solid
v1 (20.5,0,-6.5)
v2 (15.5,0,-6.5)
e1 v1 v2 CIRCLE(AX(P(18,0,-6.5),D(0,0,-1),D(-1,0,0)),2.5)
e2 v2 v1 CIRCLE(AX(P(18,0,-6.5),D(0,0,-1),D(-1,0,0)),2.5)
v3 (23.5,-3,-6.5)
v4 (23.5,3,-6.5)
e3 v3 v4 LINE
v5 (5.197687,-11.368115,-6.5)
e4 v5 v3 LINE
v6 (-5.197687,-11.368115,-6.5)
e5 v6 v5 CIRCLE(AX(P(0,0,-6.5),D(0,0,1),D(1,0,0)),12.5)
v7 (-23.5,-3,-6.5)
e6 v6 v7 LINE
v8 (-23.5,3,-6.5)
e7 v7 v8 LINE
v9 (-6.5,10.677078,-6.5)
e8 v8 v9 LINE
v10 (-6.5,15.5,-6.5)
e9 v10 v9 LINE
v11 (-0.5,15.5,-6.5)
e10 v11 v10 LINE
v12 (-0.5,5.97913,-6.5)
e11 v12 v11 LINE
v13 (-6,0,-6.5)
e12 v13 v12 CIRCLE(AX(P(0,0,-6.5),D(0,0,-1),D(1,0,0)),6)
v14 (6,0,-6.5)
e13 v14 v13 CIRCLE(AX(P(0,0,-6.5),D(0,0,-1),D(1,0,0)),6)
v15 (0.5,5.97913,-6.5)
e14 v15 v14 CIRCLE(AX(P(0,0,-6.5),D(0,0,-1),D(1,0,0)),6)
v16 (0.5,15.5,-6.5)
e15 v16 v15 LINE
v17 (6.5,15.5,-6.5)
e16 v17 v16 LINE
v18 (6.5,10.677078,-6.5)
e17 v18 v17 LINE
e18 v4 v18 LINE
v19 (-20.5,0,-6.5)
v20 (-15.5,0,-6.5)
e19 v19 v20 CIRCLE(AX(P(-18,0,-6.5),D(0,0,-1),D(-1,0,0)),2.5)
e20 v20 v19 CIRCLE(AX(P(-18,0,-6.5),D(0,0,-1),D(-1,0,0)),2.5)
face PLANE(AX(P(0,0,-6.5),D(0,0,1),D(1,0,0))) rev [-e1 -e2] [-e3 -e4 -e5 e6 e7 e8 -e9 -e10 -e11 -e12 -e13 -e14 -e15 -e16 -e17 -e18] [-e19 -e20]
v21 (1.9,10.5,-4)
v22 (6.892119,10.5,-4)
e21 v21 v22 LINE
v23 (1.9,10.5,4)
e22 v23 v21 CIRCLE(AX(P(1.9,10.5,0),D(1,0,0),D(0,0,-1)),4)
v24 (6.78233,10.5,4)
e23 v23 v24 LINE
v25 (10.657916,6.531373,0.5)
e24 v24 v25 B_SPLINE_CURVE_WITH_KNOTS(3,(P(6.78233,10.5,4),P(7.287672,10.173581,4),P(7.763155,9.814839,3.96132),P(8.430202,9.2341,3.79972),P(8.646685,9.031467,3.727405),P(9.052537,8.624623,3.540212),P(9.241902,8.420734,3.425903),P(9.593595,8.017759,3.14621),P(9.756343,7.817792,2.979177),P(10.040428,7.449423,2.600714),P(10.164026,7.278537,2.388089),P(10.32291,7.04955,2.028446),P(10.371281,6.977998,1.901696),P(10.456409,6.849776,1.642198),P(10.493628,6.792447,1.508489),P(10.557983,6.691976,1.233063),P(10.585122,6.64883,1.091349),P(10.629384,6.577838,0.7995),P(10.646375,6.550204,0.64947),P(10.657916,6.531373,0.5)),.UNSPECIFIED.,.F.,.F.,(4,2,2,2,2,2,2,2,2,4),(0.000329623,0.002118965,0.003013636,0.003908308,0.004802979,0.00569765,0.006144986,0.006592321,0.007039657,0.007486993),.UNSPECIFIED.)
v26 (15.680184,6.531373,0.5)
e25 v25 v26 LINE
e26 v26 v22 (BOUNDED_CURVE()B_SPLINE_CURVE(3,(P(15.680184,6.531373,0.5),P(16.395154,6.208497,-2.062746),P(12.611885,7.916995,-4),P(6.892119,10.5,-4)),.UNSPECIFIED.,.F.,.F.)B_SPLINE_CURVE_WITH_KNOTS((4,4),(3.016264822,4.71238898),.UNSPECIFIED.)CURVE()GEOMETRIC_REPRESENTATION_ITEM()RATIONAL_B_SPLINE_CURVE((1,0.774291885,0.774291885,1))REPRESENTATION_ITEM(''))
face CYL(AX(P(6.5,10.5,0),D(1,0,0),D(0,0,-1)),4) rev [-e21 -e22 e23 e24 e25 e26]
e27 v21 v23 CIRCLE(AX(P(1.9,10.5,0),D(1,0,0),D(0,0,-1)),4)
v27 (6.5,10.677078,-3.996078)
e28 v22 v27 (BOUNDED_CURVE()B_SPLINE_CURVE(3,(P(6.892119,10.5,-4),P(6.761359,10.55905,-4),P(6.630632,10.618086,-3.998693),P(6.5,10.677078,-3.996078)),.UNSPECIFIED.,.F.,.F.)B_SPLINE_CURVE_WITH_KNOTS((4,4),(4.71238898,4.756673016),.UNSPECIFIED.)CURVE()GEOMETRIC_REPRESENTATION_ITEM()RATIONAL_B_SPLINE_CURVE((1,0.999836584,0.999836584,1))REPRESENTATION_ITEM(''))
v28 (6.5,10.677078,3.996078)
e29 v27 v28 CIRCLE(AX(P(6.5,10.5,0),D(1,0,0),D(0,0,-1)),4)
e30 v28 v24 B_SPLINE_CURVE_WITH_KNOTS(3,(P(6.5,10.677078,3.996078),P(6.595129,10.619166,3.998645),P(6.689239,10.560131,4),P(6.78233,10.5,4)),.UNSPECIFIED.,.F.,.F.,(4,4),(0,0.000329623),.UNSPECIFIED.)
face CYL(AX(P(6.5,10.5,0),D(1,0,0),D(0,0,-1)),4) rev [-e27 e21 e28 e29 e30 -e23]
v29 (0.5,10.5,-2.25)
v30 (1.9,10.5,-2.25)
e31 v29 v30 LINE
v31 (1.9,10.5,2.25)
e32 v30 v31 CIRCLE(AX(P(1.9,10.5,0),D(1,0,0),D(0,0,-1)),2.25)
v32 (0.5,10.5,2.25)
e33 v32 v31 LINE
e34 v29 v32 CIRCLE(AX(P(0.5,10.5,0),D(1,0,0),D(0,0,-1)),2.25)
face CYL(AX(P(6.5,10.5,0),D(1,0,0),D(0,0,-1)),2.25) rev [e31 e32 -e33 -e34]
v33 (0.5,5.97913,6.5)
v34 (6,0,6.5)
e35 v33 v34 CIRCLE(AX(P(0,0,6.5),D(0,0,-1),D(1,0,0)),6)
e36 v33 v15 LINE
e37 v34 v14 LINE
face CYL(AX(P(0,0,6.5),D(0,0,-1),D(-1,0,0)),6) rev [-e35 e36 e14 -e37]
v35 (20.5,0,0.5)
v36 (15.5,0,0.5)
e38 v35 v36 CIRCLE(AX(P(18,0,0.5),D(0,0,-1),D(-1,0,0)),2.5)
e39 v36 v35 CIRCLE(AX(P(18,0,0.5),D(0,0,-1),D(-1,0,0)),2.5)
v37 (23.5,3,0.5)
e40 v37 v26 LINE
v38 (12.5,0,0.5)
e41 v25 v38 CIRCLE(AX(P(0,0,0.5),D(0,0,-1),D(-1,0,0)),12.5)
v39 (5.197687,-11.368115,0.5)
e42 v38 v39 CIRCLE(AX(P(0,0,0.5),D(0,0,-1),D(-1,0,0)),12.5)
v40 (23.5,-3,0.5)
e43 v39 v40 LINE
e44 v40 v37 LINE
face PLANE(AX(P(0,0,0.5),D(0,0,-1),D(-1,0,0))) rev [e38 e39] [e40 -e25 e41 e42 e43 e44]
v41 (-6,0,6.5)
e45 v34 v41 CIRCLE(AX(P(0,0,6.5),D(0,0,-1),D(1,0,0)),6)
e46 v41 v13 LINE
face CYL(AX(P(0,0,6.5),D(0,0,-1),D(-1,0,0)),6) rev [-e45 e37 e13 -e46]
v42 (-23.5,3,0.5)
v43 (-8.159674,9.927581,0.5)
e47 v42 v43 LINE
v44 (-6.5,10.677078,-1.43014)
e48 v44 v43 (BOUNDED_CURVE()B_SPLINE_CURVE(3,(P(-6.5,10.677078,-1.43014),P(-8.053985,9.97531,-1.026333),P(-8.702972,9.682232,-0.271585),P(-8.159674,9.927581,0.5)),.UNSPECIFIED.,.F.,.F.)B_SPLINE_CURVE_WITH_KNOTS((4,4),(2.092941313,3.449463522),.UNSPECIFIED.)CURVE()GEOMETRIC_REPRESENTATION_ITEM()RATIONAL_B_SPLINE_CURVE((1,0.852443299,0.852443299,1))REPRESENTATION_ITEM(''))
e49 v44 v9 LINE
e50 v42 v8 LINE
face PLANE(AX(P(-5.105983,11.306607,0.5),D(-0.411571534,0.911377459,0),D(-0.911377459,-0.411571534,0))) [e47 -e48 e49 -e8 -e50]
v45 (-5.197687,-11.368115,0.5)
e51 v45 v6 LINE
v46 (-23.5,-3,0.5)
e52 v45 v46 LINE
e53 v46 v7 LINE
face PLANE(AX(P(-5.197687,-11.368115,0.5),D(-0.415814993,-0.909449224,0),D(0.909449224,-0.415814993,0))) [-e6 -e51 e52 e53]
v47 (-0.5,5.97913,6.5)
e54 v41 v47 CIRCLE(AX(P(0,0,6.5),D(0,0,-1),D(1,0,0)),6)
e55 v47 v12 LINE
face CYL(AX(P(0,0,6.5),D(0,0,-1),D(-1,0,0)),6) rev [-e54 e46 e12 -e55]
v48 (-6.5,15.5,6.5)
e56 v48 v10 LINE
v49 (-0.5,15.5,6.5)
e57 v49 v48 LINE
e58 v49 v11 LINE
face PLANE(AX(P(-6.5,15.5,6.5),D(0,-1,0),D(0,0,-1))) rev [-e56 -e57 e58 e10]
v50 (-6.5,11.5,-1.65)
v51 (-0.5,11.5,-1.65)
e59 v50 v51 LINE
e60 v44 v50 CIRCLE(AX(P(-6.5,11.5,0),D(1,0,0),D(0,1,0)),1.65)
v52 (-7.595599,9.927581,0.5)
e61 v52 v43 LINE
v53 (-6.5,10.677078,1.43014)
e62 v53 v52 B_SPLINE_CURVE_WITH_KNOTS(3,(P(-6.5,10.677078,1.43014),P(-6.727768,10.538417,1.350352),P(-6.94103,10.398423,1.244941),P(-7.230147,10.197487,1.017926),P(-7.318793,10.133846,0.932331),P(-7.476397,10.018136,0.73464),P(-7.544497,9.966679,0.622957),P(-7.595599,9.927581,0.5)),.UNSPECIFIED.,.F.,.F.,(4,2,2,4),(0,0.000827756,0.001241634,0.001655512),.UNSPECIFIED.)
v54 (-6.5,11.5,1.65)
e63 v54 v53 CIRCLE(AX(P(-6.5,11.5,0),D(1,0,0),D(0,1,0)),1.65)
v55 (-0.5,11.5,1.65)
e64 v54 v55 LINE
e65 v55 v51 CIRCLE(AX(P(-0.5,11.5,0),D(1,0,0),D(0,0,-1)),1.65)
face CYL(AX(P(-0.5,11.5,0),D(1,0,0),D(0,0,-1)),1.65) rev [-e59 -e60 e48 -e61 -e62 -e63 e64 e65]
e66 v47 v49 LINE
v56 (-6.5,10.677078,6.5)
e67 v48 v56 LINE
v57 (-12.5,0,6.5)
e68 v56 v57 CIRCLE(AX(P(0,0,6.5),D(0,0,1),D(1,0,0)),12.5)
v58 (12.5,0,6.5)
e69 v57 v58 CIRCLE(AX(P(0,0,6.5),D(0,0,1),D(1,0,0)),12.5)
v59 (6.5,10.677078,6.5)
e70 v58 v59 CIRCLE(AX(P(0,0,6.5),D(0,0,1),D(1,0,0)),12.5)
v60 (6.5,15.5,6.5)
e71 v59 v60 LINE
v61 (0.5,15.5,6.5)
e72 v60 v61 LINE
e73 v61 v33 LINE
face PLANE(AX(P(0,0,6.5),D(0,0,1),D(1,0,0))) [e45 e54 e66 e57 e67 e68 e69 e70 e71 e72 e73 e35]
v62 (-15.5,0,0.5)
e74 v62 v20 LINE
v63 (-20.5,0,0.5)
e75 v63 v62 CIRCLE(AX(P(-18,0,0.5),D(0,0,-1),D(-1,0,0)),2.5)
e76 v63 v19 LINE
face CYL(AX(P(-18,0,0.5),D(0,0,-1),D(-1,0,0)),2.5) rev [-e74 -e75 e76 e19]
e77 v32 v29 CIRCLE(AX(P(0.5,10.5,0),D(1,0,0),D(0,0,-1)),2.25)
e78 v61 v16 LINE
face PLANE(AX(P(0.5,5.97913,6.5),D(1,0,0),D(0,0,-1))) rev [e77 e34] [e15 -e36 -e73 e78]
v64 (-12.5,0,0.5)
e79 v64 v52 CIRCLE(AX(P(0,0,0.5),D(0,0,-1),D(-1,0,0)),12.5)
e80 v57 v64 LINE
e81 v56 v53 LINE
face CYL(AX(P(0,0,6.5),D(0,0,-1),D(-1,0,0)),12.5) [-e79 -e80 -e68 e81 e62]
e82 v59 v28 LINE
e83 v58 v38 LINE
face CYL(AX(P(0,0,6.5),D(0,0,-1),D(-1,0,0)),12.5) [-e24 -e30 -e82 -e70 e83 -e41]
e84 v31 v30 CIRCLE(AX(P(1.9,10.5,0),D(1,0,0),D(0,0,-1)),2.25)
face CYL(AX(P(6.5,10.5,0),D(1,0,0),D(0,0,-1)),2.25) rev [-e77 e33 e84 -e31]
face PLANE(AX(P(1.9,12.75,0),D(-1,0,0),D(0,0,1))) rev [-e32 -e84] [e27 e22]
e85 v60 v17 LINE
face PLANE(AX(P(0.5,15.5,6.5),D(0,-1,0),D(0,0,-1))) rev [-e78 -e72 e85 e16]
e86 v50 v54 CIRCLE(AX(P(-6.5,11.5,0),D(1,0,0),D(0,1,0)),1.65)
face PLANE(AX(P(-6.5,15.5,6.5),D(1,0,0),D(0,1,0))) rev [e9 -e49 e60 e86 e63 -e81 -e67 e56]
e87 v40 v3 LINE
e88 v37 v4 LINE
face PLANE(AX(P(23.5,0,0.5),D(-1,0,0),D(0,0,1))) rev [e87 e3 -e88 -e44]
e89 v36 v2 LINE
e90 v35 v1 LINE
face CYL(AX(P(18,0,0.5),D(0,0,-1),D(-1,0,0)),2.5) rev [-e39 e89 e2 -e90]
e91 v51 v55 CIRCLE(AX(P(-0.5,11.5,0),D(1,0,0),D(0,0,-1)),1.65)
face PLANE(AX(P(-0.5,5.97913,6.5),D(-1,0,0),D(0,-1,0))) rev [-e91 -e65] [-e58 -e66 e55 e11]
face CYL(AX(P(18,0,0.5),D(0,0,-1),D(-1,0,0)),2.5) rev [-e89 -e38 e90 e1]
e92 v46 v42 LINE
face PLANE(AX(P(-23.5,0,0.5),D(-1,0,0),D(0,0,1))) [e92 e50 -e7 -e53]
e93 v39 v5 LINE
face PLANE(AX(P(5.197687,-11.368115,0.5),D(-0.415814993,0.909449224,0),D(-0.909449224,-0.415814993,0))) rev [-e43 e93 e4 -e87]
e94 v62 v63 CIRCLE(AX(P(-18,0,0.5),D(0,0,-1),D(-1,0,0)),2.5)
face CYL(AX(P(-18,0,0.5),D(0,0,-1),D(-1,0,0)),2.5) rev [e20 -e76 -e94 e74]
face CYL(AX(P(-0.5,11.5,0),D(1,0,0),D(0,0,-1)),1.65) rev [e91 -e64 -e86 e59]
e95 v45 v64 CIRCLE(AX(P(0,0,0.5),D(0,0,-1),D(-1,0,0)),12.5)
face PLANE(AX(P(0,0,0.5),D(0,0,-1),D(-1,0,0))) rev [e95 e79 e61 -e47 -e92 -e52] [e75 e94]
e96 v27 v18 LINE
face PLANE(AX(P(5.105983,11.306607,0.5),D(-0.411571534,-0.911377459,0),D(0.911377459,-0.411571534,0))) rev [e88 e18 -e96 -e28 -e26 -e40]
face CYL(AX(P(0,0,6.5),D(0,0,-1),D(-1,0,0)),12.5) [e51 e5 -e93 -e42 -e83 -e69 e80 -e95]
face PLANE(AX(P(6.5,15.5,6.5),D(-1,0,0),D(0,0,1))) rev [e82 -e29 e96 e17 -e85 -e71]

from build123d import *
from build123d.topology import SkipClean

# Parameters (mm, degrees)
EXTRUDE_1_DEPTH     = 6.5
EXTRUDE_START       = -7
SKETCH_2_R          = 2.5
EXTRUDE_2_DEPTH     = 7
SKETCH_3_W          = 1.65
SKETCH_3_H          = 23
CUT_EXTRUDE_START   = 10
CUT_EXTRUDE_1_DEPTH = 10


with BuildPart() as part:
    # 草图1 → 凸台-拉伸1 (new, symmetric)
    with BuildSketch(Plane.XY):
        with BuildLine():
            Line((0.5, 5.979130372), (0.5, 15.5))
            Line((0.5, 15.5), (6.5, 15.5))
            Line((6.5, 15.5), (6.5, 10.677078252))
            ThreePointArc((6.5, 10.677078252), (0, -12.5), (-6.5, 10.677078252))
            Line((-6.5, 10.677078252), (-6.5, 15.5))
            Line((-6.5, 15.5), (-0.5, 15.5))
            Line((-0.5, 15.5), (-0.5, 5.979130372))
            ThreePointArc((-0.5, 5.979130372), (0, -6), (0.5, 5.979130372))
        make_face()
    extrude(amount=EXTRUDE_1_DEPTH, both=True)

    # 草图2 → 凸台-拉伸2 (add)
    # profile 1 of 2: a face of its own
    with BuildSketch(Plane(origin=(0, 0, -6.5), x_dir=(-1, 0, 0), z_dir=(0, 0, -1)).offset(EXTRUDE_START)):
        with BuildLine():
            Line((-23.5, -3), (-5.197687408, -11.368115306))
            ThreePointArc((-5.197687408, -11.368115306), (-12.478245567, -0.737148272), (-6.5, 10.677078252))
            Line((-6.5, 10.677078252), (-23.5, 3))
            Line((-23.5, 3), (-23.5, -3))
        make_face()
        with Locations((-18, 0)):
            Circle(SKETCH_2_R, mode=Mode.SUBTRACT)
    # profile 2 of 2: a face of its own
    with BuildSketch(Plane(origin=(0, 0, -6.5), x_dir=(-1, 0, 0), z_dir=(0, 0, -1)).offset(EXTRUDE_START)):
        with BuildLine():
            ThreePointArc((6.5, 10.677078252), (12.478245567, -0.737148272), (5.197687408, -11.368115306))
            Line((5.197687408, -11.368115306), (23.5, -3))
            Line((23.5, -3), (23.5, 3))
            Line((23.5, 3), (6.5, 10.677078252))
        make_face()
        with Locations((18, 0)):
            Circle(SKETCH_2_R, mode=Mode.SUBTRACT)
    extrude(amount=EXTRUDE_2_DEPTH)

    # 草图3 → M4 螺纹孔1 (revolve, cut)
    with BuildSketch(Plane(origin=(-0.5, 11.5, 0), x_dir=(0, 0, -1), z_dir=(0, 1, 0))):
        with Locations((0.825, 11.5)):
            Rectangle(SKETCH_3_W, SKETCH_3_H)
    revolve(axis=Axis((5.85, 11.5, 0), (-1, 0, 0)), mode=Mode.SUBTRACT)

    # 草图5 → 打孔尺寸(%根据)内六角圆柱头螺钉的类型1 (revolve, cut)
    with BuildSketch(Plane(origin=(6.5, 10.5, 0), x_dir=(0, 0, -1), z_dir=(0, 1, 0))):
        Polygon((0, 0), (0, 7.351936393), (2.25, 6), (2.25, 4.6), (4, 4.6), (4, 0), align=None)
    revolve(axis=Axis((12.85, 10.5, 0), (-1, 0, 0)), mode=Mode.SUBTRACT)

    # 草图7 → 切除-拉伸1 (cut)
    with SkipClean():  # the faces are left unmerged after this step: merging them gives an invalid solid
        with BuildSketch(Plane(origin=(6.5, 0, 0), x_dir=(0, 0, -1), z_dir=(1, 0, 0)).offset(CUT_EXTRUDE_START)):
            with BuildLine():
                Line((-0.5, 10.677078252), (-3.996078489, 10.677078252))
                ThreePointArc((-3.996078489, 10.677078252), (0, 6.5), (3.996078489, 10.677078252))
                Line((3.996078489, 10.677078252), (-0.5, 10.677078252))
            make_face()
        extrude(amount=-CUT_EXTRUDE_1_DEPTH, mode=Mode.SUBTRACT)


solid = part.part
